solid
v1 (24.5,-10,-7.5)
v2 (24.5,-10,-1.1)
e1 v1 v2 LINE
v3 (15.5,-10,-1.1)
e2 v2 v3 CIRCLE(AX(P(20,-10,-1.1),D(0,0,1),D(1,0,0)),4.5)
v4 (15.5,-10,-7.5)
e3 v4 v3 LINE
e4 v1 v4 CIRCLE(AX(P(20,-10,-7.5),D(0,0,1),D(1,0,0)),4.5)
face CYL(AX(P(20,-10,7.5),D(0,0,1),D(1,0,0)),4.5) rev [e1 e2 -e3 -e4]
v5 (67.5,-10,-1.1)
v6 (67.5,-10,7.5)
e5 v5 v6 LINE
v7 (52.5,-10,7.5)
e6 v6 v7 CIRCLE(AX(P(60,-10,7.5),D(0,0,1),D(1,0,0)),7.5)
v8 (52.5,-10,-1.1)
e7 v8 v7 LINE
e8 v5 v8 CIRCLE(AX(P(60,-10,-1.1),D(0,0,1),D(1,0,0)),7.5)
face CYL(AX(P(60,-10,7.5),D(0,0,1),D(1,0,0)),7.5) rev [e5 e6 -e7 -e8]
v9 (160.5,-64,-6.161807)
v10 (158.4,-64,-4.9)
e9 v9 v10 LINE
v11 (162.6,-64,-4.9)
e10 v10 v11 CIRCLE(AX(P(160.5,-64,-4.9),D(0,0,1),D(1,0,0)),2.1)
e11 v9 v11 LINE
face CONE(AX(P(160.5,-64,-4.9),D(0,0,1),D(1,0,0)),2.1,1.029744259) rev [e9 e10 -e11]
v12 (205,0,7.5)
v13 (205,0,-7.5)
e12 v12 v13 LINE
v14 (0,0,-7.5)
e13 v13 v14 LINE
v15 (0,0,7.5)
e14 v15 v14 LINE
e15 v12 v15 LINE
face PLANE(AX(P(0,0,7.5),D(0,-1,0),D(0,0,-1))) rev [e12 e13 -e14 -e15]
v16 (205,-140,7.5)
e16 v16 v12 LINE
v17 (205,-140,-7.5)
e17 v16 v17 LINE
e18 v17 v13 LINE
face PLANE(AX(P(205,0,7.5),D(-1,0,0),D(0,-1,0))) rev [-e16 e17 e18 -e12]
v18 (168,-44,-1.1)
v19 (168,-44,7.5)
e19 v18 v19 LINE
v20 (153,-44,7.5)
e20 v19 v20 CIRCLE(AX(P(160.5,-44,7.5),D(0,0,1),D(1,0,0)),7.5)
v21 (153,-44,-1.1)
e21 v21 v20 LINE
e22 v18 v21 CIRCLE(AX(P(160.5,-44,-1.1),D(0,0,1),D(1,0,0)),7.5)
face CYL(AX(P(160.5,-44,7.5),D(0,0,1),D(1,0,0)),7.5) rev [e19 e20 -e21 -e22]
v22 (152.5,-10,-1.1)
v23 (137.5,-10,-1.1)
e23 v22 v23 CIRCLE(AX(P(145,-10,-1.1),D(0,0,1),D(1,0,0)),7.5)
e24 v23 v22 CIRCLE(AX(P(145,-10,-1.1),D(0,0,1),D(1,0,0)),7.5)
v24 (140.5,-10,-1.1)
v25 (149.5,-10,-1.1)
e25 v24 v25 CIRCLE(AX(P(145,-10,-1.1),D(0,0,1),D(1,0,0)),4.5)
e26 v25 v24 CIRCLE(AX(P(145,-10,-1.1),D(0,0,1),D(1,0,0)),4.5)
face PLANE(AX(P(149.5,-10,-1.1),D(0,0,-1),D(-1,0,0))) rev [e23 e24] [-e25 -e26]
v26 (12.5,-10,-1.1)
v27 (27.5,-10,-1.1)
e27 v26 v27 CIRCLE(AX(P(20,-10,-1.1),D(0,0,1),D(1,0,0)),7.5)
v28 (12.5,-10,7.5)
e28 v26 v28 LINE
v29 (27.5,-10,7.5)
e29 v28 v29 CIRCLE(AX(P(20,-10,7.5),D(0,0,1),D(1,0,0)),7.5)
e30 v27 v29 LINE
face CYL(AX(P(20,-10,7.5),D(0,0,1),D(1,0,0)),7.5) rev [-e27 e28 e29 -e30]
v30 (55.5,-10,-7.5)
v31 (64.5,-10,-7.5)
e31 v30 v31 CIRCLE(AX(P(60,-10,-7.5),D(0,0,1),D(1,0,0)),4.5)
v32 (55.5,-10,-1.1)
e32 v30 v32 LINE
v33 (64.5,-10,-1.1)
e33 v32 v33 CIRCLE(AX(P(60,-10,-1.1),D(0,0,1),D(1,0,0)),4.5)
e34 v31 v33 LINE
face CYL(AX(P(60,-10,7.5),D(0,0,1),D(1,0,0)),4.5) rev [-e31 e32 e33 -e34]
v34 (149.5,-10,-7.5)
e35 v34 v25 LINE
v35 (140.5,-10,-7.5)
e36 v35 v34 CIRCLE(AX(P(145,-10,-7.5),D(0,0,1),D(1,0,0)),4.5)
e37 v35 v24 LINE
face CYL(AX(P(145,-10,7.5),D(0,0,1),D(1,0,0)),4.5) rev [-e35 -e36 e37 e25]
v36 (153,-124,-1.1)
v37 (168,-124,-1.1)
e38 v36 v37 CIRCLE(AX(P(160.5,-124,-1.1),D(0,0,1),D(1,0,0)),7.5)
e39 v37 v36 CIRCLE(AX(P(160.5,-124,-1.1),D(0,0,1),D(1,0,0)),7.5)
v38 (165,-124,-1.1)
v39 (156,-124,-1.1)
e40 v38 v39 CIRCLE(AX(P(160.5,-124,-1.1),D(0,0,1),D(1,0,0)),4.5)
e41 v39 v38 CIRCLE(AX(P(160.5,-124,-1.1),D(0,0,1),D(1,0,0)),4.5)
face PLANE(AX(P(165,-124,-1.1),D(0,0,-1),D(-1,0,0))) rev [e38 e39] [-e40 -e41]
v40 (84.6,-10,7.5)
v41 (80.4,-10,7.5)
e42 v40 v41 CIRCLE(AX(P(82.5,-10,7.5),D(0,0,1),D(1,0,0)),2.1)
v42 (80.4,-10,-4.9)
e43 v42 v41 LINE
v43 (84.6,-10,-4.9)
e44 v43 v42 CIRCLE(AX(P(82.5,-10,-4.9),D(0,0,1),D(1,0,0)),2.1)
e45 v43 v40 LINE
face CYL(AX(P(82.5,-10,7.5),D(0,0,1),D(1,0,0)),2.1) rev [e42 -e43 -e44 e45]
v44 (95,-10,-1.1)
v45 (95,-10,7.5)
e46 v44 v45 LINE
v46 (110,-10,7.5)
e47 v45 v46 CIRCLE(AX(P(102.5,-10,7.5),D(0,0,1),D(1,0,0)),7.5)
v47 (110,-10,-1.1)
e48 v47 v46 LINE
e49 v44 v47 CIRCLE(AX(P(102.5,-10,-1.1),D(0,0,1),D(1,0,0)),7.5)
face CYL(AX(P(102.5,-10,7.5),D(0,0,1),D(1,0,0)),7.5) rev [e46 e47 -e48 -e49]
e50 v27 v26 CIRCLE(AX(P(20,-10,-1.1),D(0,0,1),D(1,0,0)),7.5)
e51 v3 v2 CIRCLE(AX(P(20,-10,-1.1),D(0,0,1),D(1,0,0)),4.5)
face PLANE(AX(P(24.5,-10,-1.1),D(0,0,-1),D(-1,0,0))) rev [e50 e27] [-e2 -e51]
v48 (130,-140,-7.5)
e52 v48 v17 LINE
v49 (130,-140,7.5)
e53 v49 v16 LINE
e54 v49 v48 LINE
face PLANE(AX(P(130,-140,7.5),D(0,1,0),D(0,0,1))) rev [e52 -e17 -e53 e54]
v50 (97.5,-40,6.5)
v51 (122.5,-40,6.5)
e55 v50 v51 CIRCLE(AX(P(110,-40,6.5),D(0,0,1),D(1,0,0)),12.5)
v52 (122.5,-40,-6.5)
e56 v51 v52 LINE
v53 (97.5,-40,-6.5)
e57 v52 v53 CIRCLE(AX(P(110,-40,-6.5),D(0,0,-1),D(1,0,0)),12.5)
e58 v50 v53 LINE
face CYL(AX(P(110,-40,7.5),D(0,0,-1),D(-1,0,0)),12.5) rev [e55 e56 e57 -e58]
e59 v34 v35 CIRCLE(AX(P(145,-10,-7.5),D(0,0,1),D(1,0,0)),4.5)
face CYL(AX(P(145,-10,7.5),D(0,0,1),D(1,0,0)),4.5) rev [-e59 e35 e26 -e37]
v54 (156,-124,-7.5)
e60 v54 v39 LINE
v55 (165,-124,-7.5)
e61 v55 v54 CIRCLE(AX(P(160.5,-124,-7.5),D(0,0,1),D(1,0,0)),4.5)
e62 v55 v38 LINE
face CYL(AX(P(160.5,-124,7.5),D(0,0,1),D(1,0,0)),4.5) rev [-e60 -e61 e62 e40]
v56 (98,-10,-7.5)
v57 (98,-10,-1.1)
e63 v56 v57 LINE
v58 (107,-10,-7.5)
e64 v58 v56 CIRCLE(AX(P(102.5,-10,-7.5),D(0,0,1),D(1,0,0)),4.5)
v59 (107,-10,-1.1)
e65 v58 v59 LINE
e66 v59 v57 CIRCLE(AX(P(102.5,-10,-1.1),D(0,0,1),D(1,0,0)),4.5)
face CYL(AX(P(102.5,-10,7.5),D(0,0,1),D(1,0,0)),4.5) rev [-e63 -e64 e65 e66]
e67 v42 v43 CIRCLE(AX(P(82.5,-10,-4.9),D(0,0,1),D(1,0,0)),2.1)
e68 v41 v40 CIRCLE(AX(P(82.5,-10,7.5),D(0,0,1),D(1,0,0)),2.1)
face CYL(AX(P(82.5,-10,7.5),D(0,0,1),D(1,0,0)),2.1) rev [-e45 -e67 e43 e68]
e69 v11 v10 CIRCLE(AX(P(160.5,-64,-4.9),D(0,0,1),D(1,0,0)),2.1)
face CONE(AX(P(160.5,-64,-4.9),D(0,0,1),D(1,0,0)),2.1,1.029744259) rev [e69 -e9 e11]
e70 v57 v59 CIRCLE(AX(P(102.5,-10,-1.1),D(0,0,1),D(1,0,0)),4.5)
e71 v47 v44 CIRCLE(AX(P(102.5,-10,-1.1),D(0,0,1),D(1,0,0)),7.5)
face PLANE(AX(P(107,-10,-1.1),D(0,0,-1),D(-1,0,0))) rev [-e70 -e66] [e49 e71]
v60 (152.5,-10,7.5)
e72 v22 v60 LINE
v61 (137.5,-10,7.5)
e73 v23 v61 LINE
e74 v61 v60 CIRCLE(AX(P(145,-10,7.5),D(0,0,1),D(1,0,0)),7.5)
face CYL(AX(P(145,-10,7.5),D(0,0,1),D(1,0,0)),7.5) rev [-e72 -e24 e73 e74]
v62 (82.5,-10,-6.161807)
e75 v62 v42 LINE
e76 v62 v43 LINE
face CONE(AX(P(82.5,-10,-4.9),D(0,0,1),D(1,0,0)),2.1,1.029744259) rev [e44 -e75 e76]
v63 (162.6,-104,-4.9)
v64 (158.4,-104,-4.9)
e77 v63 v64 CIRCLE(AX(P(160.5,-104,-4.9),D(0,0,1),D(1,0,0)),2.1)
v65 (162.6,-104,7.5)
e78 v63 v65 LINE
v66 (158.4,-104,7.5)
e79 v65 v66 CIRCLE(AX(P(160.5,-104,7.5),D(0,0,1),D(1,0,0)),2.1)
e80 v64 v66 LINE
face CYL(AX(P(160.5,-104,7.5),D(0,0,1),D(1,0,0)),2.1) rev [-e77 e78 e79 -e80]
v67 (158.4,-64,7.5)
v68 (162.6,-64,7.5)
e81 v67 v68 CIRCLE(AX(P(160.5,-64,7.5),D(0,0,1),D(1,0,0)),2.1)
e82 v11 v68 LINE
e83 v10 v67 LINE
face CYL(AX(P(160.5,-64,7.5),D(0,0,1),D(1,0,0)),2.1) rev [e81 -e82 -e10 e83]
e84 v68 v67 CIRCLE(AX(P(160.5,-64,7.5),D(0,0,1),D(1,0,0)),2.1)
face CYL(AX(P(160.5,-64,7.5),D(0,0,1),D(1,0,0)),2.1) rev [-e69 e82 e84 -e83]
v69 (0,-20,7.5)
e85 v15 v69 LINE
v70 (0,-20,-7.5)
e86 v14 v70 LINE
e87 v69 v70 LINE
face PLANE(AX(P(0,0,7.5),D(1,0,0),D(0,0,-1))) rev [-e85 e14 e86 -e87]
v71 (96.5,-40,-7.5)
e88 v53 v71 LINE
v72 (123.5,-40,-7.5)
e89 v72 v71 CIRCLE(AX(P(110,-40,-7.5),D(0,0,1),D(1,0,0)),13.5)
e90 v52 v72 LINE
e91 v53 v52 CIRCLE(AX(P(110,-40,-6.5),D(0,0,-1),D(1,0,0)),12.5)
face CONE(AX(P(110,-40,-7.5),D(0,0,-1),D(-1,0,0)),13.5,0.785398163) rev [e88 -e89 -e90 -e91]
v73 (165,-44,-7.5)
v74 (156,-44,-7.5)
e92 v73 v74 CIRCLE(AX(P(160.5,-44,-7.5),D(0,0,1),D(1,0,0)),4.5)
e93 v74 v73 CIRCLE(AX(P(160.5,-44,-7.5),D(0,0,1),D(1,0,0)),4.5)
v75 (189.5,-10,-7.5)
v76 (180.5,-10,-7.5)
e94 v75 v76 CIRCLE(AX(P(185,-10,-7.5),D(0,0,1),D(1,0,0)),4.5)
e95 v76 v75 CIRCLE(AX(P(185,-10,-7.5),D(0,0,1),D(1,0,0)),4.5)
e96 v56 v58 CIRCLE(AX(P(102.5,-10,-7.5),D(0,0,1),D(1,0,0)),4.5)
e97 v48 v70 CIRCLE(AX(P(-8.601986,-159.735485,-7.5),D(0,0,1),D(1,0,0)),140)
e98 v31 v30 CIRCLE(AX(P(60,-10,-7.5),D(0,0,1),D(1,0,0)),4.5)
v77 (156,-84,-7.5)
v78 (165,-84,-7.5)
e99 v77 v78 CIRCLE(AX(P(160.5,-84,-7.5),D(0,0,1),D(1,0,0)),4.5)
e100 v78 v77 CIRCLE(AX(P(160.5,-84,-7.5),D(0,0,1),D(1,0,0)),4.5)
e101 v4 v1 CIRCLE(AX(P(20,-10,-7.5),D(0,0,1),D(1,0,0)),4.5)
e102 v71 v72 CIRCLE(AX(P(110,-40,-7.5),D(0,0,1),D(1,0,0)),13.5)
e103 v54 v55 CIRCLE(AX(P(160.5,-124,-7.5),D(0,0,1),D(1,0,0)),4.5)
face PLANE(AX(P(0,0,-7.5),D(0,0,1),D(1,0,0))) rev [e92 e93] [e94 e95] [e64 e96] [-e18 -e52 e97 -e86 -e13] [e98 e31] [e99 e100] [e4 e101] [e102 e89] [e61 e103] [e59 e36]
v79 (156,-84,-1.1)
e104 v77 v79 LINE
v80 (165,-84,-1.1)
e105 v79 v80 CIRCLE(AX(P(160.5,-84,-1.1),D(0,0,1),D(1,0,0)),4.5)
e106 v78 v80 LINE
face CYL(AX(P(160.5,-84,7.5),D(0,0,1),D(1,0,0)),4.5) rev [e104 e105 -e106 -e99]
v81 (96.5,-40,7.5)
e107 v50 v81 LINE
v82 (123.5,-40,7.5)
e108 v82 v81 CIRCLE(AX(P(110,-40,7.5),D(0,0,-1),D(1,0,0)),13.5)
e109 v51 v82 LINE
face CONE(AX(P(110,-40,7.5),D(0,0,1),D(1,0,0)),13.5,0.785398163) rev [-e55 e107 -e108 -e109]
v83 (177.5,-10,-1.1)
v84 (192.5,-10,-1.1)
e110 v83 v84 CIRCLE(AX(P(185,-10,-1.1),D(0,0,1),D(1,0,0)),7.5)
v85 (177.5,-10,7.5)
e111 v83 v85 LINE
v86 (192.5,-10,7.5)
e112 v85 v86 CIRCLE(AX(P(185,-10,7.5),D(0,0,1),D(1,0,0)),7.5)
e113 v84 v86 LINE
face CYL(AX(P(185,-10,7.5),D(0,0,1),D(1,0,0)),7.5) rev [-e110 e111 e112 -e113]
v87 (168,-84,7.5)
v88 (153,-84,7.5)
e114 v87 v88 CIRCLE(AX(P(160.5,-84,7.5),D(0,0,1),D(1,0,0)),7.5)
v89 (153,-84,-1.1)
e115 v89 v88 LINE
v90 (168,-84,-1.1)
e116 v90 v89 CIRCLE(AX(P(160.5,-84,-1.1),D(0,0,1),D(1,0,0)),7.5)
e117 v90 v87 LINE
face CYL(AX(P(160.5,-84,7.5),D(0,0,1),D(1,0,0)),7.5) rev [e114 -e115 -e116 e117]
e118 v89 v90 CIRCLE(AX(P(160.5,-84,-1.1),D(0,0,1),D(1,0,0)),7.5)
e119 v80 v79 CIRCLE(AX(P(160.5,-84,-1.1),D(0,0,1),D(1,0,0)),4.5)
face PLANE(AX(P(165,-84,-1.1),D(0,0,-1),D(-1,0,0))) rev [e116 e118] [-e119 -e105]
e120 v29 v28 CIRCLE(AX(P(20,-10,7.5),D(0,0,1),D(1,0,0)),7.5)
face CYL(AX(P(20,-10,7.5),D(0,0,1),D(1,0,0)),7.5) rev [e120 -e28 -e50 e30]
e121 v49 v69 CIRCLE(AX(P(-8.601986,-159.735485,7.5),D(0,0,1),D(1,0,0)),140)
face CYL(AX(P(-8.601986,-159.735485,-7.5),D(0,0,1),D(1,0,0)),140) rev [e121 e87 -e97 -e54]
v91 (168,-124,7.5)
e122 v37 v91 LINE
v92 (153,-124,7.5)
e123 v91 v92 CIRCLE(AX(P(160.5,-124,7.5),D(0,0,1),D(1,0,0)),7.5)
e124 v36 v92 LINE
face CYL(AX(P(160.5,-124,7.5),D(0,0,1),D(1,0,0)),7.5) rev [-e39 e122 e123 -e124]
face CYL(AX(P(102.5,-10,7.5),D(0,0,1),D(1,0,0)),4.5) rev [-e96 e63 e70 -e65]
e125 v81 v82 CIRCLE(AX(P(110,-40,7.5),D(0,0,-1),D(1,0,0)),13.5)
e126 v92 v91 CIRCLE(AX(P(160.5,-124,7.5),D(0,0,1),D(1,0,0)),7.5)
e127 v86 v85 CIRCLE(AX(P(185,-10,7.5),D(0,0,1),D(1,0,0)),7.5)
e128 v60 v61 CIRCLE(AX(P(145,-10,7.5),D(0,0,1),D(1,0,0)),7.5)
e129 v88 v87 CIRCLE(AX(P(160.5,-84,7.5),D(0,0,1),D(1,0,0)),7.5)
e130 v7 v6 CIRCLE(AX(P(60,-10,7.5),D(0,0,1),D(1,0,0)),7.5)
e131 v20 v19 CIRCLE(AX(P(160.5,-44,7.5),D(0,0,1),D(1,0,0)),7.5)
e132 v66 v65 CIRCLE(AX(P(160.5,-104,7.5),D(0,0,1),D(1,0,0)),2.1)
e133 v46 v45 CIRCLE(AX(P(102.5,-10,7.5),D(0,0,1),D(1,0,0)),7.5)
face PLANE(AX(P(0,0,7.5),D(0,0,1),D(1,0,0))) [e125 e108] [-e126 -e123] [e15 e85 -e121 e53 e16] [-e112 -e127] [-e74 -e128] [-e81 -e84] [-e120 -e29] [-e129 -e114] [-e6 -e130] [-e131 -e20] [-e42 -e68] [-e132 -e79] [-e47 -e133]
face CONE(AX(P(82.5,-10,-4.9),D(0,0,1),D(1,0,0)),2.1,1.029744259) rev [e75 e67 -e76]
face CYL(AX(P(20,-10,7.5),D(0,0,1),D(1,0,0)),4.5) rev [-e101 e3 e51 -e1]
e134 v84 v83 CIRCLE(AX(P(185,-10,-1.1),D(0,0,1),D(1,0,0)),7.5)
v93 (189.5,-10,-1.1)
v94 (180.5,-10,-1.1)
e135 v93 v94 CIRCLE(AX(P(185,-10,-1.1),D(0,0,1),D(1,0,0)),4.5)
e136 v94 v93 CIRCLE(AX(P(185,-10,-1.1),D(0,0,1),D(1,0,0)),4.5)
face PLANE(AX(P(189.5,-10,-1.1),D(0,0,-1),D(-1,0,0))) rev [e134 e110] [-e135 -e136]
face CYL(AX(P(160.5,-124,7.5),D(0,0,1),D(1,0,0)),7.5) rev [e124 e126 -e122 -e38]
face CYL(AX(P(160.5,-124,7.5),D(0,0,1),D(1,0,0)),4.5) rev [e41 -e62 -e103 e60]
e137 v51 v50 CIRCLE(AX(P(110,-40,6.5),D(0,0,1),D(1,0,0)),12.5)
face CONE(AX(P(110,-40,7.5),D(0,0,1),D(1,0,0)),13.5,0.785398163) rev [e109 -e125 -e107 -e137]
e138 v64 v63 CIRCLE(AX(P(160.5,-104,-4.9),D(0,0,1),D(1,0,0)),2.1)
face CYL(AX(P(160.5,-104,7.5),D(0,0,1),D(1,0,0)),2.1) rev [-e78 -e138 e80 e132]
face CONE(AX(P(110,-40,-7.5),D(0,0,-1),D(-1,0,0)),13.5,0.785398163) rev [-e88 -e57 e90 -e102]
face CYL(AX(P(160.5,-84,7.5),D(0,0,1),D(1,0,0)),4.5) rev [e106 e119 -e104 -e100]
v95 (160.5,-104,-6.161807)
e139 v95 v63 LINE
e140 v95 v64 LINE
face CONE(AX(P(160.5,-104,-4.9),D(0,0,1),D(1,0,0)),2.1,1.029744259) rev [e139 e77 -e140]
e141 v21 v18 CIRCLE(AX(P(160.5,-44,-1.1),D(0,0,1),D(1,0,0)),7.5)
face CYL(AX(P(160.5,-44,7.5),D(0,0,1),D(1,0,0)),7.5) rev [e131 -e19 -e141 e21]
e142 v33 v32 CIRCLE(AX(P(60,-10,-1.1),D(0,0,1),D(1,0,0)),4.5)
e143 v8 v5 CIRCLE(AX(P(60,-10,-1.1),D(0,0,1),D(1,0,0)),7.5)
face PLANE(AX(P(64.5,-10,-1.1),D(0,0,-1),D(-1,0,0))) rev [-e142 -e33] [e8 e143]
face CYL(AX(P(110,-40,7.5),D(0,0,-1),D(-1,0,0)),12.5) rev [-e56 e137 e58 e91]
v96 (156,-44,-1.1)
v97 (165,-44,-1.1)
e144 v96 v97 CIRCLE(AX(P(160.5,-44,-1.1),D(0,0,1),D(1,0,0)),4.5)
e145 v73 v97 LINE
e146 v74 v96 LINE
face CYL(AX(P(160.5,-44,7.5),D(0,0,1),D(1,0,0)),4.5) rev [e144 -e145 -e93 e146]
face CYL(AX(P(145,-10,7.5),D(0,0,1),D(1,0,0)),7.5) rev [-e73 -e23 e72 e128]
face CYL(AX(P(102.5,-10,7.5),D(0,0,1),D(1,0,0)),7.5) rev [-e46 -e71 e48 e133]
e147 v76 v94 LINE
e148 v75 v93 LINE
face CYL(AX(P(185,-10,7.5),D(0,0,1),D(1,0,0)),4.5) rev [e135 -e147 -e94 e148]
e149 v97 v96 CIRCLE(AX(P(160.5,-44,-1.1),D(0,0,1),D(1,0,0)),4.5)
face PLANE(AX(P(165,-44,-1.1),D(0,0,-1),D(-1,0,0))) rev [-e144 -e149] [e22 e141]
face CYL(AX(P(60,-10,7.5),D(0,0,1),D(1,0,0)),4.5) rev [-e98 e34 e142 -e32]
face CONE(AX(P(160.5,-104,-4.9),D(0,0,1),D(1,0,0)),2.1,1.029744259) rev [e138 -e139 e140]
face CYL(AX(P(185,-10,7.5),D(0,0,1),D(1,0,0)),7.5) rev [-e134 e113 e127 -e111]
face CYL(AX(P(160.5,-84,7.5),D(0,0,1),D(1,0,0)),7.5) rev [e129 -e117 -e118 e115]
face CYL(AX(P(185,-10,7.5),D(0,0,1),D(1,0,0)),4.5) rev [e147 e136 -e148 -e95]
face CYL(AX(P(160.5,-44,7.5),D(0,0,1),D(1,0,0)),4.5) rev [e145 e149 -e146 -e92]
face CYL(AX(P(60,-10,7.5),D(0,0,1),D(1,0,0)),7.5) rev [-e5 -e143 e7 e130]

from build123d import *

# Parameters (mm, degrees)
EXTRUDE_1_DEPTH              = 7.5
HOLE_WIZARD_M8_2_D           = 9
HOLE_WIZARD_M8_2_CBORE_D     = 15
HOLE_WIZARD_M8_2_CBORE_DEPTH = 8.6
HOLE_WIZARD_M5_1_D           = 4.2
HOLE_WIZARD_M5_1_DEPTH       = 12.4
HOLE_WIZARD_M5_1_TIP         = 1.2618073
SKETCH_11_R                  = 140
CUT_EXTRUDE_2_DEPTH          = 249.696602309
SKETCH_12_R                  = 12.5
CUT_EXTRUDE_3_DEPTH          = 326.153809758
CHAMFER_1_SIZE               = 1


with BuildPart() as part:
    # 草图1 → 凸台-拉伸1 (new, symmetric)
    with BuildSketch(Plane.XY):
        Polygon((0, 0), (205, 0), (205, -140), (130, -140), (0, -20), align=None)
    extrude(amount=EXTRUDE_1_DEPTH, both=True)

    # M8 六角凹头螺钉的柱形沉头孔2 (through all)
    with Locations(Plane.XY.offset(7.5)):
        with Locations((20, -10), (60, -10), (145, -10), (102.5, -10), (185, -10), (160.5, -44), (160.5, -84), (160.5, -124)):
            CounterBoreHole(HOLE_WIZARD_M8_2_D / 2, HOLE_WIZARD_M8_2_CBORE_D / 2, HOLE_WIZARD_M8_2_CBORE_DEPTH)

    # M5 螺纹孔1
    with Locations(Plane.XY.offset(7.5)):
        with Locations((82.5, -10), (143.75, -10), (160.5, -64), (160.5, -104)):
            Hole(HOLE_WIZARD_M5_1_D / 2, depth=HOLE_WIZARD_M5_1_DEPTH)
            with Locations((0, 0, -(HOLE_WIZARD_M5_1_DEPTH + HOLE_WIZARD_M5_1_TIP / 2))):  # 118° drill point
                Cone(0, HOLE_WIZARD_M5_1_D / 2, HOLE_WIZARD_M5_1_TIP, mode=Mode.SUBTRACT)

    # 草图11 → 切除-拉伸2 (cut, through all)
    with BuildSketch(Plane.XY.offset(7.5)):
        with Locations((-8.60198636, -159.735485224)):
            Circle(SKETCH_11_R)
    extrude(amount=-CUT_EXTRUDE_2_DEPTH, mode=Mode.SUBTRACT)

    # 草图12 → 切除-拉伸3 (cut, through all)
    with BuildSketch(Plane(origin=(0, 0, -202.5), x_dir=(-1, 0, 0), z_dir=(0, 0, -1))):
        with Locations((-110, -40)):
            Circle(SKETCH_12_R)
    extrude(amount=-CUT_EXTRUDE_3_DEPTH, mode=Mode.SUBTRACT)

    # 倒角1
    chamfer_1_edges = [part.edges().sort_by_distance(p)[0] for p in [
        (122.5, -40, 7.5),
        (122.5, -40, -7.5),
    ]]
    chamfer(chamfer_1_edges, length=CHAMFER_1_SIZE)


solid = part.part
